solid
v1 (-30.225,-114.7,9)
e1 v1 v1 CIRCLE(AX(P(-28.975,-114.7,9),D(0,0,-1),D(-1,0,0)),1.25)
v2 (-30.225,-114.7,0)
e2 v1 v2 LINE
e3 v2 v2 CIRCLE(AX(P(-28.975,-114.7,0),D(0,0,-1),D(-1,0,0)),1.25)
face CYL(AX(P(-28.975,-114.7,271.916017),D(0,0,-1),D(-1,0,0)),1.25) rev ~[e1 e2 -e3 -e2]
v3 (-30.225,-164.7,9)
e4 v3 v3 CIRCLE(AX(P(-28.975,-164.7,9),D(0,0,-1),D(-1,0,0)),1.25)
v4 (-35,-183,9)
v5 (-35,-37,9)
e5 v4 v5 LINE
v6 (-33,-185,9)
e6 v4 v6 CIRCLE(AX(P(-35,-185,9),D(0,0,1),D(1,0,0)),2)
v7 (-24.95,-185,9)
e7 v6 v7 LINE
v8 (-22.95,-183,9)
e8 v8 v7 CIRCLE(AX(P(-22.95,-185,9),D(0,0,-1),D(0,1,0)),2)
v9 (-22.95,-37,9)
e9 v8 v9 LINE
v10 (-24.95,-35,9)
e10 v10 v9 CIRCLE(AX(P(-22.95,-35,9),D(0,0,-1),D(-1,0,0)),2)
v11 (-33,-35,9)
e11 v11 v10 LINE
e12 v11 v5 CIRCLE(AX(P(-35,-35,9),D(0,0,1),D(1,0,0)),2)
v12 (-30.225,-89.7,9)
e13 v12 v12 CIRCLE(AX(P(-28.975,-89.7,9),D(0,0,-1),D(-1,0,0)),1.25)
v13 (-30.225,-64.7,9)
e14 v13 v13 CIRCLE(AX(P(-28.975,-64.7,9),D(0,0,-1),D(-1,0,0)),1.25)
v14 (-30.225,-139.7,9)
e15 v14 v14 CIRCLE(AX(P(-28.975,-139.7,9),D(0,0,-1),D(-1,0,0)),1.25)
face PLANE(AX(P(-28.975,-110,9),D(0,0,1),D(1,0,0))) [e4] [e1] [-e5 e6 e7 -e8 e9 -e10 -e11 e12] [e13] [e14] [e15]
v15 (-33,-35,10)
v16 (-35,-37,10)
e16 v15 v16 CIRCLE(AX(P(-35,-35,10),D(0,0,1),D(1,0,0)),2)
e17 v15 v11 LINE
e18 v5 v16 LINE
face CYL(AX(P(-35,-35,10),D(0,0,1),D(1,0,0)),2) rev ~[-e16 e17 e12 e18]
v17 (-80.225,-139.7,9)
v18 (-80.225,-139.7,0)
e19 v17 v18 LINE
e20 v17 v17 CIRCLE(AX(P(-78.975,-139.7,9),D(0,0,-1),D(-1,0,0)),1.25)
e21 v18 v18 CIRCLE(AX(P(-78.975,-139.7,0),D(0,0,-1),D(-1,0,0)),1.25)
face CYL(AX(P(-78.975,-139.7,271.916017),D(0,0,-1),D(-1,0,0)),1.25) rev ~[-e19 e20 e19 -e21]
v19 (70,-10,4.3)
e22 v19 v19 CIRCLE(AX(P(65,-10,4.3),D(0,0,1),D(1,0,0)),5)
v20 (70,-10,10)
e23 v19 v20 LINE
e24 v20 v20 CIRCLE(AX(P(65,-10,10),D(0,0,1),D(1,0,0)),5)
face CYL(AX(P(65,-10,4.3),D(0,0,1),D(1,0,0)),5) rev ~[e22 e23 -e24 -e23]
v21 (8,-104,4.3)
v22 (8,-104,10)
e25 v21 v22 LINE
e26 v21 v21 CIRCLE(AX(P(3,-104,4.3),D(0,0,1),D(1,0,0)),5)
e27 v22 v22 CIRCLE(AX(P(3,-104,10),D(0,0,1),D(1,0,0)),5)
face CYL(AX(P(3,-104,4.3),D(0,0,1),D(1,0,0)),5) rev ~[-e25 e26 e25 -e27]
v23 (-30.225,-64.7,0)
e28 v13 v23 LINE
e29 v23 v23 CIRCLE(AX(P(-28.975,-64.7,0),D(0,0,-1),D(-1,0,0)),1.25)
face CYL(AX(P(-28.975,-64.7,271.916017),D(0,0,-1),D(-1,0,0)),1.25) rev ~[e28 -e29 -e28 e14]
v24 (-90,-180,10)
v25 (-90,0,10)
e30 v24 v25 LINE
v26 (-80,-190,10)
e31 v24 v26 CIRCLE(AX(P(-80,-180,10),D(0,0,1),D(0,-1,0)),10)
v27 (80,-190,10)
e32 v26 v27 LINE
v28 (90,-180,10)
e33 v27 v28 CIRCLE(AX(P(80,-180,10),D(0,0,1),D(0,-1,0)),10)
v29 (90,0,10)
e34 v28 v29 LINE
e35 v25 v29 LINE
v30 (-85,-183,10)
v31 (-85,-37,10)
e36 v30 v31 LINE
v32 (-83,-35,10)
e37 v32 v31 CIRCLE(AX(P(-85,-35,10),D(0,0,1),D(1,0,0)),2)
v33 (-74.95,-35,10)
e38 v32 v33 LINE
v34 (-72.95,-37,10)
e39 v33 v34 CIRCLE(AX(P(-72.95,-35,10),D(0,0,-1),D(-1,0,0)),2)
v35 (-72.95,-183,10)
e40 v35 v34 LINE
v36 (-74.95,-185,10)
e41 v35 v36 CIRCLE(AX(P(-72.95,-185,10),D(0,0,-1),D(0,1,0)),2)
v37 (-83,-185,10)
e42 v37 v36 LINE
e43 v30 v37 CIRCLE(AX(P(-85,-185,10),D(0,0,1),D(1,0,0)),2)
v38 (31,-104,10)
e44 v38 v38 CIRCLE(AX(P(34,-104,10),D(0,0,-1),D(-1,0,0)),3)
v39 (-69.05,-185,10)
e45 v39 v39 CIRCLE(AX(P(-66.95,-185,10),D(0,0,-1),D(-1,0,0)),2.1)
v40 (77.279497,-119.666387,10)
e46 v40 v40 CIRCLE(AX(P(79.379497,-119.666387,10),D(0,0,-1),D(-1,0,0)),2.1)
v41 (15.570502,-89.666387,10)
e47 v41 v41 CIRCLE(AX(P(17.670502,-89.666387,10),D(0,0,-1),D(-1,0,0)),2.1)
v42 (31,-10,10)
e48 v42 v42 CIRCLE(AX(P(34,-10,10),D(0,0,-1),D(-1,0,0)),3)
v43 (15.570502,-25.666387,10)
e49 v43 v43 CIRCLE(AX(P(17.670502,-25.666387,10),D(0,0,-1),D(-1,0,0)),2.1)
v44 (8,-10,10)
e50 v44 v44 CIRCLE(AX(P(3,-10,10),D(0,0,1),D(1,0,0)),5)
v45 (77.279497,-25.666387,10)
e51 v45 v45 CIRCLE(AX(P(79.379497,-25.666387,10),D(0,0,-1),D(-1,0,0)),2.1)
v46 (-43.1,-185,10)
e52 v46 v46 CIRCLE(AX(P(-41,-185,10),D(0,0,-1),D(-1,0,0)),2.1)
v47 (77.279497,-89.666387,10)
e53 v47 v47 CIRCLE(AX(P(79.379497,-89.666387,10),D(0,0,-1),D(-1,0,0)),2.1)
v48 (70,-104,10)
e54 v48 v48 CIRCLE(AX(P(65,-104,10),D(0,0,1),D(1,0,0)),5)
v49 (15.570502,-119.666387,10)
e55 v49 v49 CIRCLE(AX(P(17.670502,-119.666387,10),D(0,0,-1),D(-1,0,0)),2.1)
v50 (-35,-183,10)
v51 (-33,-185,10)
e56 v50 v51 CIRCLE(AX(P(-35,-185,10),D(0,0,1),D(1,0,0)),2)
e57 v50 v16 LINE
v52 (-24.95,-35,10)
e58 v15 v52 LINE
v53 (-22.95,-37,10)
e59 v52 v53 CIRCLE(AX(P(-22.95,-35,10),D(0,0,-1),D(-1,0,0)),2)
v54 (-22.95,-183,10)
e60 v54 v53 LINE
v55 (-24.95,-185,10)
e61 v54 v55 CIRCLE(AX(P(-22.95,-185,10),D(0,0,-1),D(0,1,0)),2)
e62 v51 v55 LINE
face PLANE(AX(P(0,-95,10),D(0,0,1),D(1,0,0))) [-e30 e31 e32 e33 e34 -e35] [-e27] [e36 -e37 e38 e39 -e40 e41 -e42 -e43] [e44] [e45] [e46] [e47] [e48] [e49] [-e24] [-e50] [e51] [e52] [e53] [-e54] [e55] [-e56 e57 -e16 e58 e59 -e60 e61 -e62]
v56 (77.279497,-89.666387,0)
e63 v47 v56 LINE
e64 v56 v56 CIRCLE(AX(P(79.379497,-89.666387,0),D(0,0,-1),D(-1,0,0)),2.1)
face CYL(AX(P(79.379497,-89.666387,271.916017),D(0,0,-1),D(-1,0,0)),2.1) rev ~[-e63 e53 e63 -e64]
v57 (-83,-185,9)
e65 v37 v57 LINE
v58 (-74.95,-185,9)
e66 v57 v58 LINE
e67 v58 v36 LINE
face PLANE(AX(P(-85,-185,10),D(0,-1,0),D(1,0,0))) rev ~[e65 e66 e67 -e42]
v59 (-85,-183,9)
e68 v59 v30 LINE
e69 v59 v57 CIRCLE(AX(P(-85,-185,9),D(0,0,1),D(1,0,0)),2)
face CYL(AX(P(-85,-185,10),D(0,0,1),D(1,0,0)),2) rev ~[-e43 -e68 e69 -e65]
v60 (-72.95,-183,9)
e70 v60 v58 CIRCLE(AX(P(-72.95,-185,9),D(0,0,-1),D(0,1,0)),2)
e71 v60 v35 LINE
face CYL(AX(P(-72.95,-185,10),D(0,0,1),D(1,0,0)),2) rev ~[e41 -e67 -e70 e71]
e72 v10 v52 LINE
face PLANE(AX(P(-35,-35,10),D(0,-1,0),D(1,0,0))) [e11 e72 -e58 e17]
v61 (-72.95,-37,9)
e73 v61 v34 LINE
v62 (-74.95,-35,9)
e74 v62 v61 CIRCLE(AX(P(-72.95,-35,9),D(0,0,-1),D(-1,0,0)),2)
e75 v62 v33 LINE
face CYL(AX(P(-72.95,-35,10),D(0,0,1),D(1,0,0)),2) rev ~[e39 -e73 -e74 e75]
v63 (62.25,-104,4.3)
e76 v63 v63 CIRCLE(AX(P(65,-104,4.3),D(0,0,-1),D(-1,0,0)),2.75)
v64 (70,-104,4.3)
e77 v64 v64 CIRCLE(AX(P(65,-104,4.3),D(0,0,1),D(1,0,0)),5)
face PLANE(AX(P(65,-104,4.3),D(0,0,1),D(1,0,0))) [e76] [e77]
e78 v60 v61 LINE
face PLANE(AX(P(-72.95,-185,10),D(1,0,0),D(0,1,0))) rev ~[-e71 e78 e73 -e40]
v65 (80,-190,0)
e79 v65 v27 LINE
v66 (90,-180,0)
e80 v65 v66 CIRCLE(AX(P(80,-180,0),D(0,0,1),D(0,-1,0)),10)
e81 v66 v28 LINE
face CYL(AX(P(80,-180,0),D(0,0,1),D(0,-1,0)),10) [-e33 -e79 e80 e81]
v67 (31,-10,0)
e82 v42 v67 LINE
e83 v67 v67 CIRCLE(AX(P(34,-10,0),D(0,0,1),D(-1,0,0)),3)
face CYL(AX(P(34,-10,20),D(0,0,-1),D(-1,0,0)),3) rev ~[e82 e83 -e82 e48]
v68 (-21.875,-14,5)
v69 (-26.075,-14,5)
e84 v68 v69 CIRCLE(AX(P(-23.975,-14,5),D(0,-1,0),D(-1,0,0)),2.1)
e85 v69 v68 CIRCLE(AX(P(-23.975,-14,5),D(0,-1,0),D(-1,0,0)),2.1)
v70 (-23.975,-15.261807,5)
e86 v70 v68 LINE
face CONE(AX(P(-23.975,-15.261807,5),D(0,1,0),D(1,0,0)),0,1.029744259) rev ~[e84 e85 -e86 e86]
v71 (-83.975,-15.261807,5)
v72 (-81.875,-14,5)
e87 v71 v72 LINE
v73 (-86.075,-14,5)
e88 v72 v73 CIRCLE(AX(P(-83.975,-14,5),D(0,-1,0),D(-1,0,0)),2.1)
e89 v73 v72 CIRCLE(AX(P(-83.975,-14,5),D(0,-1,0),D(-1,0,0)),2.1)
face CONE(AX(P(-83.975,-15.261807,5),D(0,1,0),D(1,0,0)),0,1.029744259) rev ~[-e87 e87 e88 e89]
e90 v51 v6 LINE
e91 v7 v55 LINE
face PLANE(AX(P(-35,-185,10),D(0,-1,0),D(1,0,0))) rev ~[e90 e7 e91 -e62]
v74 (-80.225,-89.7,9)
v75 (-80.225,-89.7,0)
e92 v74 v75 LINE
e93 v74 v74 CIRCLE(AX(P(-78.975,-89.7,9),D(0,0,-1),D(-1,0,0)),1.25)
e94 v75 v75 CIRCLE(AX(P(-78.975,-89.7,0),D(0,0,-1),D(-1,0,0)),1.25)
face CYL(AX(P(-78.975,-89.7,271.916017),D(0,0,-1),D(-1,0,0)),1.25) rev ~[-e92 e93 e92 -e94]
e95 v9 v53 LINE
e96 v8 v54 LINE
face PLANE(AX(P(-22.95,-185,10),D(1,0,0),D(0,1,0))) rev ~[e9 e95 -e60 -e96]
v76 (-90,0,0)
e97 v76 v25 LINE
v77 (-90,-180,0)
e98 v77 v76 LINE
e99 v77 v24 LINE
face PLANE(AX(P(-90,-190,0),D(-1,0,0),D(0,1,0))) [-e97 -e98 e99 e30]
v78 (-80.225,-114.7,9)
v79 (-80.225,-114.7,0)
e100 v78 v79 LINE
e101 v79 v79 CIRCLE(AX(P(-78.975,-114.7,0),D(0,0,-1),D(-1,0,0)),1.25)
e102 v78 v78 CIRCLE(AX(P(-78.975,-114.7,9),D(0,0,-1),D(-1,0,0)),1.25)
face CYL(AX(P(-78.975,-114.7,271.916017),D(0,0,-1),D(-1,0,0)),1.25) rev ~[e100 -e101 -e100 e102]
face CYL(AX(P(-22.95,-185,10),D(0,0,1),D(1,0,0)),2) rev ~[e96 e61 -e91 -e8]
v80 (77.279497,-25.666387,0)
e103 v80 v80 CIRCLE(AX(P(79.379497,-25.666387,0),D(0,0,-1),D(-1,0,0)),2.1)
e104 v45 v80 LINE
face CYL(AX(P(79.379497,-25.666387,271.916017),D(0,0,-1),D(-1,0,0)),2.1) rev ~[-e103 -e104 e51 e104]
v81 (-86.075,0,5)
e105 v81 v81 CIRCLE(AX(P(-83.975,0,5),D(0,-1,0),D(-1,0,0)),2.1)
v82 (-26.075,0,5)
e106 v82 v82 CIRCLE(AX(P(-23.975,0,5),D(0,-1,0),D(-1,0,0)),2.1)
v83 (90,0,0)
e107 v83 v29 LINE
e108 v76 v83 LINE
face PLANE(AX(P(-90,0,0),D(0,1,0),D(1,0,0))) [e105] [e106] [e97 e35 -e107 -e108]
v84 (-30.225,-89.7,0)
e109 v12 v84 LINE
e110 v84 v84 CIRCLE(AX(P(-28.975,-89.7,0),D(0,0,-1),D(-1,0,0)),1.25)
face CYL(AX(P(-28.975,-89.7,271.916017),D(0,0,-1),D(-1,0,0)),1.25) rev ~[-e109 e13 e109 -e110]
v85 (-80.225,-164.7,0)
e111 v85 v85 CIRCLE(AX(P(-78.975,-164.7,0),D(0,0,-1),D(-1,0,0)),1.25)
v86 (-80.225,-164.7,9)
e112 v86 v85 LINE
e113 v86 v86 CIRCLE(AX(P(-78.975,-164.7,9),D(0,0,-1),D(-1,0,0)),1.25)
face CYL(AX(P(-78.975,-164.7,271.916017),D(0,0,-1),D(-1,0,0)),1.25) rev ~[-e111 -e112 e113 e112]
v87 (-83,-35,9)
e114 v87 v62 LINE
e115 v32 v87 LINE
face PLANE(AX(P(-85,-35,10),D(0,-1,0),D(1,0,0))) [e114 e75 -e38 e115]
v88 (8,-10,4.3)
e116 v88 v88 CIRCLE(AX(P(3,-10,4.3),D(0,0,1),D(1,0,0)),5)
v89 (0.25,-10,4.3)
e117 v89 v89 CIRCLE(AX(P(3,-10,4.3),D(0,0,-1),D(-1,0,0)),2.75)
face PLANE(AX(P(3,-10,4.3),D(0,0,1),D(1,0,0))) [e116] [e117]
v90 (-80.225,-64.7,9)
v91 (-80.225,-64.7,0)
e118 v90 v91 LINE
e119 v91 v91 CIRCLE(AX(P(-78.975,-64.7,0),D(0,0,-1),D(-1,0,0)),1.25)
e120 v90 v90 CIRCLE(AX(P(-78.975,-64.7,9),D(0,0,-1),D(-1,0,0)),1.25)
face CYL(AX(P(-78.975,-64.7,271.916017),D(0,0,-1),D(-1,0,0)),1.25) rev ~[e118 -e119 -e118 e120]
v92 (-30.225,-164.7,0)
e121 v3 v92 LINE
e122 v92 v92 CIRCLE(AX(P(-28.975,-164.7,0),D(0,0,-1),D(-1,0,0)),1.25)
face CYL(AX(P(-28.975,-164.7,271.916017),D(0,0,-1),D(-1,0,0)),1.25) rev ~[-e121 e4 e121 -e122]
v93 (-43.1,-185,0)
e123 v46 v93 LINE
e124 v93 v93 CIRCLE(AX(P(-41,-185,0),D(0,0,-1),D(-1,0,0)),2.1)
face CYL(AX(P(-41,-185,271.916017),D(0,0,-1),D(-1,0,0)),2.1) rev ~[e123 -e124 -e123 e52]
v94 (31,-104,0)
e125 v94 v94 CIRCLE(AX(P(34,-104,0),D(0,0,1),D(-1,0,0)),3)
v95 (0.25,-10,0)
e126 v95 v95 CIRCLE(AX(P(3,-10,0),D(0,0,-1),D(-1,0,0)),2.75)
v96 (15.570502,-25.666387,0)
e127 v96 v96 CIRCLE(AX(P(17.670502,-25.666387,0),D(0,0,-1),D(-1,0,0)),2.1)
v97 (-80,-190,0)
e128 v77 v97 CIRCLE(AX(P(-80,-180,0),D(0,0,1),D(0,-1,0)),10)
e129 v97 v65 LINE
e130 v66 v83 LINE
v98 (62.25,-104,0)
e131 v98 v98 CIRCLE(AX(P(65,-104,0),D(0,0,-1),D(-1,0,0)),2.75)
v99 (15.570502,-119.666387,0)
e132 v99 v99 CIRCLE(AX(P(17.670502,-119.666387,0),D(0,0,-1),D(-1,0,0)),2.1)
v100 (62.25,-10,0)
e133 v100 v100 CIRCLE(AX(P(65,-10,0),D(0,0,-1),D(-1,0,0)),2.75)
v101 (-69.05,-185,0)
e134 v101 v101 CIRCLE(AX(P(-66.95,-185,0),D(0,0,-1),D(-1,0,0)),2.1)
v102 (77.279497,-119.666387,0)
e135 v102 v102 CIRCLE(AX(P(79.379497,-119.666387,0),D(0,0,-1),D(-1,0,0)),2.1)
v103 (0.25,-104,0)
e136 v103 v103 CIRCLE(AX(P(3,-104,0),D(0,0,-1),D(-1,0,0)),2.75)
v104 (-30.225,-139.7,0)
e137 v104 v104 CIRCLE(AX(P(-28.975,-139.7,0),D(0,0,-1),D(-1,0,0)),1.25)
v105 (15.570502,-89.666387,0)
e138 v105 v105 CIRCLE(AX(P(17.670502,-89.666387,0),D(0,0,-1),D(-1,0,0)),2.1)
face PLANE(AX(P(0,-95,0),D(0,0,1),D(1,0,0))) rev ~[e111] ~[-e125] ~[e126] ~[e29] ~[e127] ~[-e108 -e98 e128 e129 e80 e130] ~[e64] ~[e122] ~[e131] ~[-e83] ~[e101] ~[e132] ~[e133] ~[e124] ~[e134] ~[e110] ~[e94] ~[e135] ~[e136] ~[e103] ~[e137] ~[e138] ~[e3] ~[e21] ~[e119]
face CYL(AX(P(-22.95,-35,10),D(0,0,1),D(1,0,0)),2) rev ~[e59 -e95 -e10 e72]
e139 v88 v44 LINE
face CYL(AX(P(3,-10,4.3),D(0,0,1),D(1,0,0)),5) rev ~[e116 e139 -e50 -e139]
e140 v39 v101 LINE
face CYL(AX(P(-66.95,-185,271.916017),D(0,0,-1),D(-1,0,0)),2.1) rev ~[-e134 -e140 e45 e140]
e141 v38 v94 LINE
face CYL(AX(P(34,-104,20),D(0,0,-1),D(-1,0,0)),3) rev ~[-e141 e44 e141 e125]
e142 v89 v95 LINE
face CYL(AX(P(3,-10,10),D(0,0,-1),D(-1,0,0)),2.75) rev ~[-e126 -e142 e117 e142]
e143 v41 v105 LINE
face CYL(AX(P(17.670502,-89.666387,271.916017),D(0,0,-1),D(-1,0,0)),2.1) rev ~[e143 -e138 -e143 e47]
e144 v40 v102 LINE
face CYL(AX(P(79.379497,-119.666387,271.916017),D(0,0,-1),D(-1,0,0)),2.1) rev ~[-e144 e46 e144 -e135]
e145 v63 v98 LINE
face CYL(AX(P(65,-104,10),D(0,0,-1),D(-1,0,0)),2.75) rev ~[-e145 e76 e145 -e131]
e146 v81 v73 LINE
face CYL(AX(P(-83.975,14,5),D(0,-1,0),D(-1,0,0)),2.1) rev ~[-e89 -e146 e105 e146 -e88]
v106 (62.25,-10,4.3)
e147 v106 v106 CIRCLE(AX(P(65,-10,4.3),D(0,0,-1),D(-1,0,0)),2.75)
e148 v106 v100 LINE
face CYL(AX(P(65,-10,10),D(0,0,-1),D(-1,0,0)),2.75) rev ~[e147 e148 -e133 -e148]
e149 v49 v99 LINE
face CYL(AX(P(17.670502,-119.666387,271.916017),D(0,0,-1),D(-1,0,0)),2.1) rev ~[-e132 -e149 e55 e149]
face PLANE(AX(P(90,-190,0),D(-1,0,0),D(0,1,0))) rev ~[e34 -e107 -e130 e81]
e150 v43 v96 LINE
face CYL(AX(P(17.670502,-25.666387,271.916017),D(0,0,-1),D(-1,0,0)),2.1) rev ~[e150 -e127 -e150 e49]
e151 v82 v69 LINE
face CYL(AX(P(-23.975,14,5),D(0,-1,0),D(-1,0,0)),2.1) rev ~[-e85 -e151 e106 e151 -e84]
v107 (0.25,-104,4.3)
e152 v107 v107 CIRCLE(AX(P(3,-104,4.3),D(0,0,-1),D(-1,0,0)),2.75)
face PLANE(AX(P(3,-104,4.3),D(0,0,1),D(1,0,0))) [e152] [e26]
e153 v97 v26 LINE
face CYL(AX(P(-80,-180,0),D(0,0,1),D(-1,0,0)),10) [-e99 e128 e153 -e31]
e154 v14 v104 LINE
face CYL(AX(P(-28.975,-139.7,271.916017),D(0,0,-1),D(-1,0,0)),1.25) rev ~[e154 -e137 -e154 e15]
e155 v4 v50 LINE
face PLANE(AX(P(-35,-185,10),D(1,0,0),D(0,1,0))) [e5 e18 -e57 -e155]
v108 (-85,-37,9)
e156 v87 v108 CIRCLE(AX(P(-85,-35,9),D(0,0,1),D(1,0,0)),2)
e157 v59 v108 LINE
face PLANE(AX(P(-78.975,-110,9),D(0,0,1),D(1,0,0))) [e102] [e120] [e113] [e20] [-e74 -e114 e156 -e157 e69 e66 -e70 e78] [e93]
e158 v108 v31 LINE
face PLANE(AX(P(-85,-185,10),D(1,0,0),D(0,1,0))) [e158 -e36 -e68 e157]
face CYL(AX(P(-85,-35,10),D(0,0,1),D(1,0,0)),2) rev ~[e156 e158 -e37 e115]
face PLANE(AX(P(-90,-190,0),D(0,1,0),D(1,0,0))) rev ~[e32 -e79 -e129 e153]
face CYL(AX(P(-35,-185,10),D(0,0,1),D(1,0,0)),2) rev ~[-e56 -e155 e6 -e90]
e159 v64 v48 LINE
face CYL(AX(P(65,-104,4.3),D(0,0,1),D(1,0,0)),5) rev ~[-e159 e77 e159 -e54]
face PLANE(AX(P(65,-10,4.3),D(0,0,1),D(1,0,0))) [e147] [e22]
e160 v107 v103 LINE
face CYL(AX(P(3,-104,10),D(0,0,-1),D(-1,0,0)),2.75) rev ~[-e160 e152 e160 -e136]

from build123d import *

# Parameters (mm, degrees)
SKETCH_1_W                = 180
SKETCH_1_H                = 190
EXTRUDE_1_DEPTH           = 10
HOLE_WIZARD_1_D           = 5.5
HOLE_WIZARD_1_CBORE_D     = 10
HOLE_WIZARD_1_CBORE_DEPTH = 5.7
PATTERN_LINEAR_1_COUNT    = 2
PATTERN_LINEAR_1_PITCH    = 94
SKETCH_4_W                = 12.05
SKETCH_4_H                = 150
CUT_EXTRUDE_1_DEPTH       = 1
SKETCH_6_R                = 2
CUT_EXTRUDE_2_DEPTH       = 1
HOLE_WIZARD_M5_1_D        = 4.2
HOLE_WIZARD_M5_1_DEPTH    = 14
HOLE_WIZARD_M5_1_TIP      = 1.2618073
FILLET_1_R                = 10
HOLE_WIZARD_M5_2_D        = 4.2
HOLE_WIZARD_M5_3_D        = 4.2
HOLE_WIZARD_6_0_6_1_D     = 6
HOLE_WIZARD_6_0_6_1_DEPTH = 10
HOLE_WIZARD_6_0_6_1_TIP   = 1.802581857
HOLE_WIZARD_M3_1_D        = 2.5


with BuildPart() as part:
    # 草图1 → 凸台-拉伸1 (new body)
    with BuildSketch(Plane.XY):
        with Locations((0, -95)):
            Rectangle(SKETCH_1_W, SKETCH_1_H)
    extrude(amount=EXTRUDE_1_DEPTH)

    # 打孔尺寸(%根据)开槽圆柱头螺钉的类型1 (through all)
    with Locations(Plane.XY.offset(10)):
        with Locations((65, -10), (3, -10)):
            hole_wizard_1 = CounterBoreHole(HOLE_WIZARD_1_D / 2, HOLE_WIZARD_1_CBORE_D / 2, HOLE_WIZARD_1_CBORE_DEPTH)

    # 阵列(线性)1: 打孔尺寸(%根据)开槽圆柱头螺钉的类型1 ×2
    with Locations(*[(0, -i * PATTERN_LINEAR_1_PITCH, 0) for i in range(1, PATTERN_LINEAR_1_COUNT)]):
        add(hole_wizard_1, mode=Mode.SUBTRACT)

    # 草图4 → 切除-拉伸1 (cut)
    with BuildSketch(Plane.XY.offset(10)):
        with Locations((-78.975, -110)):
            Rectangle(SKETCH_4_W, SKETCH_4_H)
        with Locations((-28.975, -110)):
            Rectangle(SKETCH_4_W, SKETCH_4_H)
    extrude(amount=-CUT_EXTRUDE_1_DEPTH, mode=Mode.SUBTRACT)

    # 草图6 → 切除-拉伸2 (cut)
    with BuildSketch(Plane.XY.offset(10)):
        with Locations((-72.95, -35)):
            Circle(SKETCH_6_R)
        with Locations((-85, -35)):
            Circle(SKETCH_6_R)
        with Locations((-85, -185)):
            Circle(SKETCH_6_R)
        with Locations((-72.95, -185)):
            Circle(SKETCH_6_R)
        with Locations((-35, -185)):
            Circle(SKETCH_6_R)
        with Locations((-22.95, -185)):
            Circle(SKETCH_6_R)
        with Locations((-35, -35)):
            Circle(SKETCH_6_R)
        with Locations((-22.95, -35)):
            Circle(SKETCH_6_R)
    extrude(amount=-CUT_EXTRUDE_2_DEPTH, mode=Mode.SUBTRACT)

    # M5 螺纹孔1
    with Locations(Plane(origin=(0, 0, 0), x_dir=(1, 0, 0), z_dir=(0, 1, 0))):
        with Locations((-23.975, -5), (-83.975, -5)):
            Hole(HOLE_WIZARD_M5_1_D / 2, depth=HOLE_WIZARD_M5_1_DEPTH)
            with Locations((0, 0, -(HOLE_WIZARD_M5_1_DEPTH + HOLE_WIZARD_M5_1_TIP / 2))):  # 118° drill point
                Cone(0, HOLE_WIZARD_M5_1_D / 2, HOLE_WIZARD_M5_1_TIP, mode=Mode.SUBTRACT)

    # 圆角1
    fillet_1_edges = [part.edges().sort_by_distance(p)[0] for p in [
        (90, -190, 5),
        (-90, -190, 5),
    ]]
    fillet(fillet_1_edges, radius=FILLET_1_R)

    # M5 螺纹孔2 (through all)
    with Locations(Plane.XY.offset(10)):
        with Locations((-66.95, -185), (-41, -185)):
            Hole(HOLE_WIZARD_M5_2_D / 2)

    # M5 螺纹孔3 (through all)
    with Locations(Plane.XY.offset(10)):
        with Locations((79.379496826, -119.666387024), (17.670502343, -119.666387024), (17.670502343, -89.666387024), (79.379496826, -89.666387024), (79.379496826, -25.666387024), (17.670502343, -25.666387024)):
            Hole(HOLE_WIZARD_M5_3_D / 2)

    # Ø6.0 (6) 直径孔1
    with Locations(Plane.XY.offset(10)):
        with Locations((34, -104), (34, -10)):
            Hole(HOLE_WIZARD_6_0_6_1_D / 2, depth=HOLE_WIZARD_6_0_6_1_DEPTH)
            with Locations((0, 0, -(HOLE_WIZARD_6_0_6_1_DEPTH + HOLE_WIZARD_6_0_6_1_TIP / 2))):  # 118° drill point
                Cone(0, HOLE_WIZARD_6_0_6_1_D / 2, HOLE_WIZARD_6_0_6_1_TIP, mode=Mode.SUBTRACT)

    # M3 螺纹孔1 (through all)
    with Locations(Plane.XY.offset(10)):
        with Locations((-28.975, -64.7), (-78.975, -64.7), (-78.975, -89.7), (-78.975, -114.7), (-78.975, -164.7), (-78.975, -139.7), (-28.975, -164.7), (-28.975, -139.7), (-28.975, -114.7), (-28.975, -89.7)):
            Hole(HOLE_WIZARD_M3_1_D / 2)


solid = part.part
